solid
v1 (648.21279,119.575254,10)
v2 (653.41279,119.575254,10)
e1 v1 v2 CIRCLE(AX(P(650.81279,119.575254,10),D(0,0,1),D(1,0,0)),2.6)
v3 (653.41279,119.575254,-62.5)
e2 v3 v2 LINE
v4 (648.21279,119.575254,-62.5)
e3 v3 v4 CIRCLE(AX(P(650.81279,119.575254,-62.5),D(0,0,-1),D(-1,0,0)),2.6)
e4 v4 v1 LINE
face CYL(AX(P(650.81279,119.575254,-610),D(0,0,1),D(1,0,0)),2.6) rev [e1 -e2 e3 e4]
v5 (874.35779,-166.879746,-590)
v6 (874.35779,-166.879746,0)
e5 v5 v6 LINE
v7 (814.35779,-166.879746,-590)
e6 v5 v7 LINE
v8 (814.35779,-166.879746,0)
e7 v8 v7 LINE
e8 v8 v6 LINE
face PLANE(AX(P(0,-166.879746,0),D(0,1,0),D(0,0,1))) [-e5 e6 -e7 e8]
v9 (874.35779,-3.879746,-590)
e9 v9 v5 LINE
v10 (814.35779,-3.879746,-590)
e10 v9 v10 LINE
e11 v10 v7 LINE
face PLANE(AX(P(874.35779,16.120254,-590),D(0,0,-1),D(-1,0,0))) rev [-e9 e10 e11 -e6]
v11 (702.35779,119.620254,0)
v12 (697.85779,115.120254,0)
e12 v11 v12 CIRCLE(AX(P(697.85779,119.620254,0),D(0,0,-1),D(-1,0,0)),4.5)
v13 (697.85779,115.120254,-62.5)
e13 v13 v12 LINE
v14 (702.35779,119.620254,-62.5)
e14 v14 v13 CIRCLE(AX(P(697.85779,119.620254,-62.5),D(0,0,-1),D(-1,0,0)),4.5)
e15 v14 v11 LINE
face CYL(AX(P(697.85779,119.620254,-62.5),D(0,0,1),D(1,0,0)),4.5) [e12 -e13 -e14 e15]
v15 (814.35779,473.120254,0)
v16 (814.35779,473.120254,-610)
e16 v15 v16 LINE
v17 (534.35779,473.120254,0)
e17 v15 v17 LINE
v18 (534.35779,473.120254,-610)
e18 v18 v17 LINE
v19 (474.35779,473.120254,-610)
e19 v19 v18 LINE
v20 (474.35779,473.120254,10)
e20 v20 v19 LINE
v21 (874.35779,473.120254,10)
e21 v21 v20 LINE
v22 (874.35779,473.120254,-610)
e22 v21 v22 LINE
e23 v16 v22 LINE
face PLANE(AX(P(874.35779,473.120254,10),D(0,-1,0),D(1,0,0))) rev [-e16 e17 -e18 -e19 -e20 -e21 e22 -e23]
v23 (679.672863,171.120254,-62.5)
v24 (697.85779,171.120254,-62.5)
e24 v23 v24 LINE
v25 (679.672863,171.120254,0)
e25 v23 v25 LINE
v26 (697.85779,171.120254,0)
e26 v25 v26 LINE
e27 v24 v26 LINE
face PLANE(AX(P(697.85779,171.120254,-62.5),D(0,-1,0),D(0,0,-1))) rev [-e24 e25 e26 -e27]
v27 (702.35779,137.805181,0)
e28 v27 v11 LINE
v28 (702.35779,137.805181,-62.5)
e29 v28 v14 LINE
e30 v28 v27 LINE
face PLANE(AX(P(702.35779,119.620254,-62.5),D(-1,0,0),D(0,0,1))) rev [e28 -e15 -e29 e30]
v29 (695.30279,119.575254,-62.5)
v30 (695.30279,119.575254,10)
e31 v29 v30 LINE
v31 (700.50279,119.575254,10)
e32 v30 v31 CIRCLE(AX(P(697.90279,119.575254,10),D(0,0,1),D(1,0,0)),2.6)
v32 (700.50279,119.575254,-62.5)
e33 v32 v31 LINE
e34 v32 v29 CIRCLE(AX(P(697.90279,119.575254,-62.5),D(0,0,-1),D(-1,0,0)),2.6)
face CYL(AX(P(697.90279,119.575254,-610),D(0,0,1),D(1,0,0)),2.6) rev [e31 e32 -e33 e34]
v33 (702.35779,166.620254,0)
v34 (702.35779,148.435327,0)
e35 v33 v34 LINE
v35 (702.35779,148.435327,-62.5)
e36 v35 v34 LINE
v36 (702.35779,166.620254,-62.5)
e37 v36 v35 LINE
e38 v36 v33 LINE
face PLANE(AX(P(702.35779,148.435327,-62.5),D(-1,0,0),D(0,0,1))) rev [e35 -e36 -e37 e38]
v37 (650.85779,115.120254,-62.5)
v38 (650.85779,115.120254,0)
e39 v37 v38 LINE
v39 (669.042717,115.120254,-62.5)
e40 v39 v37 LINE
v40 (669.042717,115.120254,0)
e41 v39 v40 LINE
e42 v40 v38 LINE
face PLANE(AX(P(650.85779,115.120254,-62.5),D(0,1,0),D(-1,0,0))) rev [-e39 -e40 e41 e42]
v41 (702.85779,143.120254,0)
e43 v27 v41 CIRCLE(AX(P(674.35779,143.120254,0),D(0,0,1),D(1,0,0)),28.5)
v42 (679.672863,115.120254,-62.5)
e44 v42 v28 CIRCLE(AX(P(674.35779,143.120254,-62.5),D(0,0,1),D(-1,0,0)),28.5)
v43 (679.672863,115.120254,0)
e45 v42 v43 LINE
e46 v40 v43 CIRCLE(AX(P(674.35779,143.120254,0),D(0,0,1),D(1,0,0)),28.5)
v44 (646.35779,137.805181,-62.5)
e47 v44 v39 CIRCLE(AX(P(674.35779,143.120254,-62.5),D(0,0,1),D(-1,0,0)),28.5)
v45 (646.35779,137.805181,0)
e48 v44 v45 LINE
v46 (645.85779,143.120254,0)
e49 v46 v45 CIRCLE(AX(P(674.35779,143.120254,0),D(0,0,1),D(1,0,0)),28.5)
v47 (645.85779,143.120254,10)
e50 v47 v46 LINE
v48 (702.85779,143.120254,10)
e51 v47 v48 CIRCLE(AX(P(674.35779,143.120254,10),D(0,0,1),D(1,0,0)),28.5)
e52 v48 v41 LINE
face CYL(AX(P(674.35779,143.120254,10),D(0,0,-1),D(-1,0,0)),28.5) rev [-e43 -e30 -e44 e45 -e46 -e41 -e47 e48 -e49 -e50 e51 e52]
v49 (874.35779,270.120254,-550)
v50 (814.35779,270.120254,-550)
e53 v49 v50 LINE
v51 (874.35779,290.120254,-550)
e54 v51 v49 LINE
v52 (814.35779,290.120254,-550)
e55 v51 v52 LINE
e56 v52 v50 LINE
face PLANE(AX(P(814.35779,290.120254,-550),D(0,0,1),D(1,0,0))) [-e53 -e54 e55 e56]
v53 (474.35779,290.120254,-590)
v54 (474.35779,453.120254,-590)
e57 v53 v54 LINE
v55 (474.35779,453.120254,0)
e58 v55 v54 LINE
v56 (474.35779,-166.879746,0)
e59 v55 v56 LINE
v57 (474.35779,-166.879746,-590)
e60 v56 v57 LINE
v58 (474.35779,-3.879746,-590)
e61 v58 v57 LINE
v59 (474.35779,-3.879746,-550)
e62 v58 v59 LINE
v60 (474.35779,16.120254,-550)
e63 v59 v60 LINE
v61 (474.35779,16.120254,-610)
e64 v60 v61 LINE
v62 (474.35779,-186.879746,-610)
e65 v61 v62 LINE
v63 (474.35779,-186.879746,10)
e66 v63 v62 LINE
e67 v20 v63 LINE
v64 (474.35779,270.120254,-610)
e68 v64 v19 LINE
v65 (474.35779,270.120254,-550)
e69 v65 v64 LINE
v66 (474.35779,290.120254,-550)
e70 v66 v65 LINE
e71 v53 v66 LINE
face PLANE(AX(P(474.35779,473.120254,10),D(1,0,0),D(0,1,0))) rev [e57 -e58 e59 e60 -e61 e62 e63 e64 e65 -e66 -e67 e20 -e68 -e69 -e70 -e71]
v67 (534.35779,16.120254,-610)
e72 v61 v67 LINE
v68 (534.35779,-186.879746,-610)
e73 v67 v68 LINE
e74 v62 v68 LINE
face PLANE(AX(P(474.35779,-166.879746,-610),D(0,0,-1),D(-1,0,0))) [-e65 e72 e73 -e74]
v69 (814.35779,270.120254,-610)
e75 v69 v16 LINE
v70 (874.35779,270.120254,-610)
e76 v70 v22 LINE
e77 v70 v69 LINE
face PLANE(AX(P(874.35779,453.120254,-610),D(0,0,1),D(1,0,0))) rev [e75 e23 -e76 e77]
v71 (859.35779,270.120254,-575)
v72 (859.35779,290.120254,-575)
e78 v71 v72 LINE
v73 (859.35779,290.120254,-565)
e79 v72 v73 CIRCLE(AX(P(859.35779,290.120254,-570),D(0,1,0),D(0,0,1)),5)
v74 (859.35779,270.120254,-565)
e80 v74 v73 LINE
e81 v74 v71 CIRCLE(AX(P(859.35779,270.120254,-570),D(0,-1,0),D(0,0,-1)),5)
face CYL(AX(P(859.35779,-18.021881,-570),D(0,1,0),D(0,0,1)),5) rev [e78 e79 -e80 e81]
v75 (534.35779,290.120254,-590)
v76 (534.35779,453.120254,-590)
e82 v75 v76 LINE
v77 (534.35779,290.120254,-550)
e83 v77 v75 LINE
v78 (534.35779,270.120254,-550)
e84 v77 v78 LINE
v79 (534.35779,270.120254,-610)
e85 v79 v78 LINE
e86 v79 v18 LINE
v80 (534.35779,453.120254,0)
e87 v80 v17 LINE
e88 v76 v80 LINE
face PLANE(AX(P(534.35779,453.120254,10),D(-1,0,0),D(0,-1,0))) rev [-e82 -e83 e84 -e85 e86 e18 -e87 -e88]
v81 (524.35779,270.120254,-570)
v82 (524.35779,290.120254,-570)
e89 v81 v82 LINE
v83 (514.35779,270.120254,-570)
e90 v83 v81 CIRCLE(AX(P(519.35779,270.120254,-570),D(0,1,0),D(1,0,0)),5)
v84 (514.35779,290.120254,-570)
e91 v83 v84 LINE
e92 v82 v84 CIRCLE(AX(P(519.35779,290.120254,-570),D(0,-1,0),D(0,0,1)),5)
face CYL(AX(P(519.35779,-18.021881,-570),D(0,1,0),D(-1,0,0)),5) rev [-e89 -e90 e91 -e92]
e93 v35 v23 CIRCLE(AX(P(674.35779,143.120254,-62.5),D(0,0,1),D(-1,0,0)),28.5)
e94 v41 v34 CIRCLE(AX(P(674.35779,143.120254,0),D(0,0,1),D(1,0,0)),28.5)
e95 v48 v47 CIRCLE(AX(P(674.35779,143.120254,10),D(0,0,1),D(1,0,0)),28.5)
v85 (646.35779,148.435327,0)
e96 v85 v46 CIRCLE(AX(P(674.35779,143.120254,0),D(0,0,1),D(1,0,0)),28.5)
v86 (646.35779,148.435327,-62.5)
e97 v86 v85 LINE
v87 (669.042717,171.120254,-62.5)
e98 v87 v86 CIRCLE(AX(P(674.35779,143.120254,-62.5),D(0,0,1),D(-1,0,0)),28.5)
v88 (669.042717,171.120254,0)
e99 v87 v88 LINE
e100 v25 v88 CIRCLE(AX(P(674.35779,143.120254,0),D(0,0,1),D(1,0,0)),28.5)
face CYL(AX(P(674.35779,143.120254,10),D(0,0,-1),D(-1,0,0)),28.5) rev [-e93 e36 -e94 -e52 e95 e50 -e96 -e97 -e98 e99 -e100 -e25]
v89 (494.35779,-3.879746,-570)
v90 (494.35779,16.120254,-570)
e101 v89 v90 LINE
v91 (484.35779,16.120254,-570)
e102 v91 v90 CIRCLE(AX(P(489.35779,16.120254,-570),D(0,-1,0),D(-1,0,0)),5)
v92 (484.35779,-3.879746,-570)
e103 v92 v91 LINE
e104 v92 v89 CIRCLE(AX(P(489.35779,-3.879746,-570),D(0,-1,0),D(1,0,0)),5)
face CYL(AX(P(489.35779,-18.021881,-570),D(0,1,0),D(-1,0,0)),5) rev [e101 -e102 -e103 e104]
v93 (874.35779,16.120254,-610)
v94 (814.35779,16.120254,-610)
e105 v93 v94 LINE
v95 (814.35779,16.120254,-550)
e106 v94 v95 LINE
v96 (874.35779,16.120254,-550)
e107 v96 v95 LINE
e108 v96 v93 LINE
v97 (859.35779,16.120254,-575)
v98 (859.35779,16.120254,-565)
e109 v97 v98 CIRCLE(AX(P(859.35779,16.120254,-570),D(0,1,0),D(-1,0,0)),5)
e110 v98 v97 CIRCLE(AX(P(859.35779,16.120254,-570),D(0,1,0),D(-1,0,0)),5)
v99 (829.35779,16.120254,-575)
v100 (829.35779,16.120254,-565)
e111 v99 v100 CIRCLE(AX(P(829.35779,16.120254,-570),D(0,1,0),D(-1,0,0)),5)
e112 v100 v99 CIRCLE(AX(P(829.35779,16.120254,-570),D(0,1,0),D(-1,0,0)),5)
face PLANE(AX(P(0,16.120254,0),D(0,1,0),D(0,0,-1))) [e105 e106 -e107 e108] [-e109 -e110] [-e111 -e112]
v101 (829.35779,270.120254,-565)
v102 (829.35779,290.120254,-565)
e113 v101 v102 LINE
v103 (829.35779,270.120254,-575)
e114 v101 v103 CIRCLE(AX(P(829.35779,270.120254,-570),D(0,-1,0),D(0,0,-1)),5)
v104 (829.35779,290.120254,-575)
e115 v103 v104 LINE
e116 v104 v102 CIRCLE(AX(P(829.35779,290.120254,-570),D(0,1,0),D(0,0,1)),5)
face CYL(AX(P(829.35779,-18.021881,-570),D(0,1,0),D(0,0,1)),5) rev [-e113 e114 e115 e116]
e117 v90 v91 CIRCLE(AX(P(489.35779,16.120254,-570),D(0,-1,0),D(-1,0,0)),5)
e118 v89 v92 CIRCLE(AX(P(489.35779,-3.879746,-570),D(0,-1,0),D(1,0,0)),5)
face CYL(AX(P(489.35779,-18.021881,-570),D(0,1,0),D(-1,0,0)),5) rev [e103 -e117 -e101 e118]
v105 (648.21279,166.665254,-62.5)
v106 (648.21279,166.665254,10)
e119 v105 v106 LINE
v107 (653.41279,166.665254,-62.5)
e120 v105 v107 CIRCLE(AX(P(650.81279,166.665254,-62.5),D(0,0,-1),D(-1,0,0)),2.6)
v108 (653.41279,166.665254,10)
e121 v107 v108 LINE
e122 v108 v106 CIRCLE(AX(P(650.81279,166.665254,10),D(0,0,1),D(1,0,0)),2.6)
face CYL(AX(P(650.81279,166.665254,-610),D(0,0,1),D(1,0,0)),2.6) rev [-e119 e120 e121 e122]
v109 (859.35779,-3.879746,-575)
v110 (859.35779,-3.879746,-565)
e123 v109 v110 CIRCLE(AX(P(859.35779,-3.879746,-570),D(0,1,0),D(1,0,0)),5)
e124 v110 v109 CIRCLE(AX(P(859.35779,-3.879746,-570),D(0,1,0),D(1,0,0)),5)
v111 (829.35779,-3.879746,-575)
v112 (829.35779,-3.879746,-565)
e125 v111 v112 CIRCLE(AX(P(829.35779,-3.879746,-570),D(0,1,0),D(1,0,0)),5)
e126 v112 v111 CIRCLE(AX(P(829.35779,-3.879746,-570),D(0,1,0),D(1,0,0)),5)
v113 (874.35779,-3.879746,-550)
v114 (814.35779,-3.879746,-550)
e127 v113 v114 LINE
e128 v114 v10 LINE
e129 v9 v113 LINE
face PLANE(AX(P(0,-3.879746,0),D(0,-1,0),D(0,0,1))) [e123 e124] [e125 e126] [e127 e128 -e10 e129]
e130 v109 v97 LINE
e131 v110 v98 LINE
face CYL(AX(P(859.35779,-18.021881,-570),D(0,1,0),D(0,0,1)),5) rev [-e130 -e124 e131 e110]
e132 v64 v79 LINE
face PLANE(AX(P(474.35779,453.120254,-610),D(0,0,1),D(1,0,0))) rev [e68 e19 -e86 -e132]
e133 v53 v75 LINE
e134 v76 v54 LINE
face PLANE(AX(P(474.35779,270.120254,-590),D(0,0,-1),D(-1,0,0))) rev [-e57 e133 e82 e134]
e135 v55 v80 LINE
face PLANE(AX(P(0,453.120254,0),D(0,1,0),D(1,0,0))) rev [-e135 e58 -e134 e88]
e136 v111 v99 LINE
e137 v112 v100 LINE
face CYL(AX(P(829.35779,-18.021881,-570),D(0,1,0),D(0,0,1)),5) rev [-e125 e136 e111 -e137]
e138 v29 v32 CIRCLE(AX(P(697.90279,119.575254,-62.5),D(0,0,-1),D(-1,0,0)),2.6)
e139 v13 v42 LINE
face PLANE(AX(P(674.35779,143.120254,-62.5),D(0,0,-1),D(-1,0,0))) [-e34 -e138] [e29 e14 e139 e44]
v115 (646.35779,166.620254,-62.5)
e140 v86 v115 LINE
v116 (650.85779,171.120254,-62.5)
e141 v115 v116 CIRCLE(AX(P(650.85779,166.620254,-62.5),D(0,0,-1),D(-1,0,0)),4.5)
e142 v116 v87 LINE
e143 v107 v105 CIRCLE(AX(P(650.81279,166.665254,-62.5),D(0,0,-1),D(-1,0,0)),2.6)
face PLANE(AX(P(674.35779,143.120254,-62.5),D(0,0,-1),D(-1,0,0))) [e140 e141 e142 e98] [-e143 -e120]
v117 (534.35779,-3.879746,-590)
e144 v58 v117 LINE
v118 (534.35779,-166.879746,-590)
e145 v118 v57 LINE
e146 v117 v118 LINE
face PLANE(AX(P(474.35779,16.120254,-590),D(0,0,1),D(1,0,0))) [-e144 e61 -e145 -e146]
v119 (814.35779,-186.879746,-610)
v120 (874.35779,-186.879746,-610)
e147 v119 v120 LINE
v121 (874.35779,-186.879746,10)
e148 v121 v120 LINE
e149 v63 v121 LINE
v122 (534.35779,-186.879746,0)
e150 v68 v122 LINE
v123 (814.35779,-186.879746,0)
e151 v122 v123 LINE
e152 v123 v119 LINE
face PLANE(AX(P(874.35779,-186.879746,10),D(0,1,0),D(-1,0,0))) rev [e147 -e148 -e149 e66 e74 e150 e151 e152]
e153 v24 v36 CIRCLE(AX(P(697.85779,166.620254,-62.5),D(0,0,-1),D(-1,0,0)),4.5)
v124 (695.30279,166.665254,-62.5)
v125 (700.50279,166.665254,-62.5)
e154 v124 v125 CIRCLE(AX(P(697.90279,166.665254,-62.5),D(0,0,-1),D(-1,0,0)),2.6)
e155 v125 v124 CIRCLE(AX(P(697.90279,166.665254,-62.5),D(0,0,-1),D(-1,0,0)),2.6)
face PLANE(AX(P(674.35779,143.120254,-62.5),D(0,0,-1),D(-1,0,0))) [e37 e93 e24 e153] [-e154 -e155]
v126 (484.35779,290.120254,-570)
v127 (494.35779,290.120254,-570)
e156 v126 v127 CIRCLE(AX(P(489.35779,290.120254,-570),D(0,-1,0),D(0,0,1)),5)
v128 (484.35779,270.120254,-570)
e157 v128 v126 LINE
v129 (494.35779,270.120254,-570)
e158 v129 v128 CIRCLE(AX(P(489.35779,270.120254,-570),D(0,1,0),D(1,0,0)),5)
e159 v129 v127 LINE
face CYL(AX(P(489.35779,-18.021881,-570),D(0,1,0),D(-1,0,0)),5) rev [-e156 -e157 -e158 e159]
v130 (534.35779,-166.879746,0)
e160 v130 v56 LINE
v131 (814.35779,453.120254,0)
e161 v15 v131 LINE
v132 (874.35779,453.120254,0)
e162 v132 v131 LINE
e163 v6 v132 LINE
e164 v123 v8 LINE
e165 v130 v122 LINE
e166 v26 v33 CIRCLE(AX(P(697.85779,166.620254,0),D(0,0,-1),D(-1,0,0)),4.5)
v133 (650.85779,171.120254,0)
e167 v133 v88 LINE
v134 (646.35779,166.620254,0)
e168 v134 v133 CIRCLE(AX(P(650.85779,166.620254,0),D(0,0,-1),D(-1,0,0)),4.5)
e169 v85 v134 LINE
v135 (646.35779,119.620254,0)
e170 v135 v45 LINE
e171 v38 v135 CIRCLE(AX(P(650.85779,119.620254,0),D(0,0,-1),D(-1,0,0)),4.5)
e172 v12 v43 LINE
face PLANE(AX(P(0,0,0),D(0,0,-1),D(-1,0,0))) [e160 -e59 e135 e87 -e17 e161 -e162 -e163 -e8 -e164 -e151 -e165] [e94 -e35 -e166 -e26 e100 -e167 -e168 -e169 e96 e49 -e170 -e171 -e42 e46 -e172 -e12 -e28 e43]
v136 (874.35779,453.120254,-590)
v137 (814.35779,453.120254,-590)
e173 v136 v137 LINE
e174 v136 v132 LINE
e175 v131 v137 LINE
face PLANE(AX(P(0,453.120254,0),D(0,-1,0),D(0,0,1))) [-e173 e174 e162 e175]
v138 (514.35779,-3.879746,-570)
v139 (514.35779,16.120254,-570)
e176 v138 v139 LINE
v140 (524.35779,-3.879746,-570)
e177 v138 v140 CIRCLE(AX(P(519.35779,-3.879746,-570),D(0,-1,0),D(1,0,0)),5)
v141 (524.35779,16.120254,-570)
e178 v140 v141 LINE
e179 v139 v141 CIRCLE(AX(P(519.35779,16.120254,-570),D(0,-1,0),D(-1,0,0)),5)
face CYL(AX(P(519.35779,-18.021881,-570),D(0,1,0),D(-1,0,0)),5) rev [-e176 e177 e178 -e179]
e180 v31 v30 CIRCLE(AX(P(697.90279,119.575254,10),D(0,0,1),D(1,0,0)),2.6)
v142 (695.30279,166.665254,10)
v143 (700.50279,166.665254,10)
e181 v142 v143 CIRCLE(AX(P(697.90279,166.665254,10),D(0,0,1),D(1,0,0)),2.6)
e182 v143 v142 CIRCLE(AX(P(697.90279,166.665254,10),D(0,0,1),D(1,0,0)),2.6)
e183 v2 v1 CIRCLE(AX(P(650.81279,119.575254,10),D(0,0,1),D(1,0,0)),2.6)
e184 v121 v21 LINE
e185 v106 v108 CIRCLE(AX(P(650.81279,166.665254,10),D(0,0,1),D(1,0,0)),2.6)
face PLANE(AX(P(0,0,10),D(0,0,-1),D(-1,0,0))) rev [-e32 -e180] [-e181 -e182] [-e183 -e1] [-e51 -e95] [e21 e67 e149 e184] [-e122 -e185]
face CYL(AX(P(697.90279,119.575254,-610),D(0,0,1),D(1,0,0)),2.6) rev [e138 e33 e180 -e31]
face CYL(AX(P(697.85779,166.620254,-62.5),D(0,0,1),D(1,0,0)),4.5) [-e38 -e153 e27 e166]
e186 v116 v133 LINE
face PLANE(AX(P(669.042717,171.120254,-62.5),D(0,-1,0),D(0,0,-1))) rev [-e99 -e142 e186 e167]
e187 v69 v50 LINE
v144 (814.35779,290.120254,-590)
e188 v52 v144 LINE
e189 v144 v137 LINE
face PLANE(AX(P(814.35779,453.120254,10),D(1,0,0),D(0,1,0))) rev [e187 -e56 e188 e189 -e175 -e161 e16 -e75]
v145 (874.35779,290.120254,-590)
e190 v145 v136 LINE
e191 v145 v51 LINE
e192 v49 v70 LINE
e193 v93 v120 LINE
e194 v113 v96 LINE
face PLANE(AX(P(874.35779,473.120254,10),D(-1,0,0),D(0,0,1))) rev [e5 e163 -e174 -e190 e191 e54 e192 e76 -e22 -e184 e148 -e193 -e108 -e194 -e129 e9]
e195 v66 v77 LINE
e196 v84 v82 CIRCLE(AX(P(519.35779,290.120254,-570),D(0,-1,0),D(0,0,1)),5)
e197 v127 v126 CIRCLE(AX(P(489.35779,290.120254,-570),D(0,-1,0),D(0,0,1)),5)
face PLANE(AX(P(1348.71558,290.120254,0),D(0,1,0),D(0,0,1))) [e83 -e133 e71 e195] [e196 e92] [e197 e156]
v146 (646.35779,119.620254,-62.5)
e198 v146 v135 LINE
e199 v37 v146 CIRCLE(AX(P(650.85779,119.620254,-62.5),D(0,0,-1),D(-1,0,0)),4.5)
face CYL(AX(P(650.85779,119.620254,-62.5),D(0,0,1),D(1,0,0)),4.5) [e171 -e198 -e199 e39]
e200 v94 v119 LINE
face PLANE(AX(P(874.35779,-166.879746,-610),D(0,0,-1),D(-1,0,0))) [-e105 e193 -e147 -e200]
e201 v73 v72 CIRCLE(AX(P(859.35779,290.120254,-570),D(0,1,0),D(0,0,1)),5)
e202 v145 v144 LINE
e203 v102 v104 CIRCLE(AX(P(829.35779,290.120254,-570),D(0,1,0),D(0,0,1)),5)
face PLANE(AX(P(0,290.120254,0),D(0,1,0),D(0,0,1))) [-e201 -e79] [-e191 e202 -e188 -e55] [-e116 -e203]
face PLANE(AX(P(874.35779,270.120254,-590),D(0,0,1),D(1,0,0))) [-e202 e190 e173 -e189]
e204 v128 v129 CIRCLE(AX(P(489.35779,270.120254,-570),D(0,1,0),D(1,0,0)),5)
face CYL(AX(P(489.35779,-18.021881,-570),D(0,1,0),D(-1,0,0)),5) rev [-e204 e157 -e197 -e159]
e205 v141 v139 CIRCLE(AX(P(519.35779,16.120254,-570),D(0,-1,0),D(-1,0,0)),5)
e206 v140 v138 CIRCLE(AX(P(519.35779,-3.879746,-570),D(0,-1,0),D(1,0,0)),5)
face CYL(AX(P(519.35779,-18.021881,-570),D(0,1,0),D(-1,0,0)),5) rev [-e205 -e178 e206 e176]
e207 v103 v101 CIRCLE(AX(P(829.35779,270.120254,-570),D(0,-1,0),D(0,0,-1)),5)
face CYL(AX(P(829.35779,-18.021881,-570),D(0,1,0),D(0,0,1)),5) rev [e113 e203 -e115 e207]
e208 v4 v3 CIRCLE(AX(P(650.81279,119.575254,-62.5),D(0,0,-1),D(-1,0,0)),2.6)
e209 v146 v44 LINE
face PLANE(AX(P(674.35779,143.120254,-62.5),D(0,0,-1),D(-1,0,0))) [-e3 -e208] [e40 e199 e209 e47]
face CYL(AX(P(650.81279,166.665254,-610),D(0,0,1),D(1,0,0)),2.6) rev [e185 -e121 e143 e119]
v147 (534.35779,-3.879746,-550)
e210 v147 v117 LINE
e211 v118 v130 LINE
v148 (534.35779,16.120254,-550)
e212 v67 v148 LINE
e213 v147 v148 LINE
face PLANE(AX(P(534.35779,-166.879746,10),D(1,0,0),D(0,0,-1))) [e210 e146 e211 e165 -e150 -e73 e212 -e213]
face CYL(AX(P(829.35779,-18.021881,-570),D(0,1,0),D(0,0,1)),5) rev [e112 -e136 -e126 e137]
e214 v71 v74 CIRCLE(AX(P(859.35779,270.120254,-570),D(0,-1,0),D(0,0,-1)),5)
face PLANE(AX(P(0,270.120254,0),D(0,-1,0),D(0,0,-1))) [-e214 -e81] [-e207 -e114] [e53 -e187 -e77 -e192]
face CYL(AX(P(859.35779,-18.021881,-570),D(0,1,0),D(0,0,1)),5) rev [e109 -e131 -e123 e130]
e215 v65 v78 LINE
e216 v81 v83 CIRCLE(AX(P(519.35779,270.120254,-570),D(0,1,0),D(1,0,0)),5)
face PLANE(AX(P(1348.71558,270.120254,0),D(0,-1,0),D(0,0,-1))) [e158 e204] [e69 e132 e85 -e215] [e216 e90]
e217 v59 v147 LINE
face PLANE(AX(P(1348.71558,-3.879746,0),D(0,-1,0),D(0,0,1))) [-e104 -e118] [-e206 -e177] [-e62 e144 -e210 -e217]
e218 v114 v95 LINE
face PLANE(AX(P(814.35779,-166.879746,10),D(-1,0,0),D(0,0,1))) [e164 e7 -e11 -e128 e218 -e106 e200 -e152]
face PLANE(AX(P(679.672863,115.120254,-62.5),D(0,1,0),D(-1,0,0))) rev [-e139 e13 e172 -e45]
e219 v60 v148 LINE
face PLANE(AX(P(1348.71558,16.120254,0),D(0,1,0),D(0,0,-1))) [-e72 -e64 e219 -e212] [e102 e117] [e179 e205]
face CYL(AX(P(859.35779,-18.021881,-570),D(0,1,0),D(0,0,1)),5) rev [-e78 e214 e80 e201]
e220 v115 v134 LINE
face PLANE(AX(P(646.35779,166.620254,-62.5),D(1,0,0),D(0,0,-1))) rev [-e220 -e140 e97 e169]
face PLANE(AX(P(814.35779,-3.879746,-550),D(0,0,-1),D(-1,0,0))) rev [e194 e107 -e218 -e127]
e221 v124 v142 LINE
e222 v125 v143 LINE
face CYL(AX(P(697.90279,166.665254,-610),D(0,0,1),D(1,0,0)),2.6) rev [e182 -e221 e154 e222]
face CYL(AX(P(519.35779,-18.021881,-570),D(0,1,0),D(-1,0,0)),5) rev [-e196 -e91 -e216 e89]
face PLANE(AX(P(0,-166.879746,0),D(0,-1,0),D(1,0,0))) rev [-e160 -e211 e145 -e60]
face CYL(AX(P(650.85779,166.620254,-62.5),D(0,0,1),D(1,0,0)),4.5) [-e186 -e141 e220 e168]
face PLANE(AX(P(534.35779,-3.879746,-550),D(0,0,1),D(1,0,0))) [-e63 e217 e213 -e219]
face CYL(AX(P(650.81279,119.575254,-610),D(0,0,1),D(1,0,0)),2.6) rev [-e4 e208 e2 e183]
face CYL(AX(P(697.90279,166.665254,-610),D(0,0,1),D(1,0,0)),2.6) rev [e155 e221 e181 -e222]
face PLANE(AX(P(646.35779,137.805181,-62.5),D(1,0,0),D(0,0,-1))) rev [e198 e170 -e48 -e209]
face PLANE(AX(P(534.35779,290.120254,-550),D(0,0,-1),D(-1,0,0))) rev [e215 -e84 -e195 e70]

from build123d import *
from build123d.topology import SkipClean

# Parameters (mm, degrees)
SKETCH_1_W                                 = 400
SKETCH_1_H                                 = 660
SKETCH_1_R                                 = 28.5
EXTRUDE_1_DEPTH                            = 10
EXTRUDE_START                              = 62.5
EXTRUDE_3_DEPTH                            = 62.5
SKETCH_4_W                                 = 60
SKETCH_4_H                                 = 620
EXTRUDE_4_DEPTH                            = 20
SKETCH_5_W                                 = 60
SKETCH_5_H                                 = 20
EXTRUDE_5_DEPTH                            = 203
MIRROR_3_COPY_1_SKETCH_W                   = 60
MIRROR_3_COPY_1_SKETCH_H                   = 20
MIRROR_3_COPY_1_DEPTH                      = 203
MIRROR_3_AT_THE_SECOND_PLANE_COPY_1_SKET_W = 60
MIRROR_3_AT_THE_SECOND_PLANE_COPY_1_SKET_H = 20
MIRROR_3_AT_THE_SECOND_PLANE_COPY_1_DEPTH  = 203
MIRROR_3_AT_THE_SECOND_PLANE_COPY_2_SKET_W = 60
MIRROR_3_AT_THE_SECOND_PLANE_COPY_2_SKET_H = 20
MIRROR_3_AT_THE_SECOND_PLANE_COPY_2_DEPTH  = 203
MIRROR_3_AT_THE_SECOND_PLANE_COPY_3_SKET_W = 60
MIRROR_3_AT_THE_SECOND_PLANE_COPY_3_SKET_H = 20
MIRROR_3_AT_THE_SECOND_PLANE_COPY_3_DEPTH  = 203
SKETCH_6_W                                 = 60
SKETCH_6_H                                 = 60
EXTRUDE_6_DEPTH                            = 20
MIRROR_5_COPY_1_SKETCH_W                   = 60
MIRROR_5_COPY_1_SKETCH_H                   = 60
MIRROR_5_COPY_1_DEPTH                      = 20
CUT_EXTRUDE_1_REACH                        = 1169.96
SKETCH_7_R                                 = 5
SKETCH_8_R                                 = 2.6
CUT_EXTRUDE_2_DEPTH                        = 1172.641719812


with BuildPart() as part:
    # 草图1 → 凸台-拉伸1 (new body)
    with BuildSketch(Plane.XY):
        with Locations((674.357789758, 143.120254367)):
            Rectangle(SKETCH_1_W, SKETCH_1_H)
        with Locations((674.357789758, 143.120254367)):
            Circle(SKETCH_1_R, mode=Mode.SUBTRACT)
    extrude(amount=EXTRUDE_1_DEPTH)

    # 草图3 → 凸台-拉伸3 (add)
    with SkipClean():  # the faces are left unmerged after this step: merging them gives an invalid solid
        with BuildSketch(Plane(origin=(0, 0, 0), x_dir=(-1, 0, 0), z_dir=(0, 0, -1)).offset(EXTRUDE_START)):
            with BuildLine():
                Line((-702.357789758, 148.435327273), (-702.357789758, 166.620254367))
                ThreePointArc((-702.357789758, 166.620254367), (-701.039770274, 169.802234882), (-697.857789758, 171.120254367))
                Line((-697.857789758, 171.120254367), (-679.672862665, 171.120254367))
                ThreePointArc((-679.672862665, 171.120254367), (-694.510333022, 163.27279763), (-702.357789758, 148.435327273))
            make_face()
            with BuildLine():
                Line((-679.672862665, 115.120254367), (-697.857789758, 115.120254367))
                ThreePointArc((-697.857789758, 115.120254367), (-701.039770274, 116.438273851), (-702.357789758, 119.620254367))
                Line((-702.357789758, 119.620254367), (-702.357789758, 137.80518146))
                ThreePointArc((-702.357789758, 137.80518146), (-694.510333022, 122.967711103), (-679.672862665, 115.120254367))
            make_face()
            with BuildLine():
                Line((-646.357789758, 137.80518146), (-646.357789758, 119.620254367))
                ThreePointArc((-646.357789758, 119.620254367), (-647.675809243, 116.438273851), (-650.857789758, 115.120254367))
                Line((-650.857789758, 115.120254367), (-669.042716852, 115.120254367))
                ThreePointArc((-669.042716852, 115.120254367), (-654.205246495, 122.967711103), (-646.357789758, 137.80518146))
            make_face()
            with BuildLine():
                Line((-669.042716852, 171.120254367), (-650.857789758, 171.120254367))
                ThreePointArc((-650.857789758, 171.120254367), (-647.675809243, 169.802234882), (-646.357789758, 166.620254367))
                Line((-646.357789758, 166.620254367), (-646.357789758, 148.435327273))
                ThreePointArc((-646.357789758, 148.435327273), (-654.205246495, 163.27279763), (-669.042716852, 171.120254367))
            make_face()
        extrude(amount=-EXTRUDE_3_DEPTH)

    # 草图4 → 凸台-拉伸4 (add)
    with SkipClean():  # the faces are left unmerged after this step: merging them gives an invalid solid
        with BuildSketch(Plane.XZ.offset(186.879745633)):
            with Locations((504.357789758, -300)):
                Rectangle(SKETCH_4_W, SKETCH_4_H)
            with Locations((844.357789758, -300)):
                Rectangle(SKETCH_4_W, SKETCH_4_H)
        extrude_4 = extrude(amount=-EXTRUDE_4_DEPTH)

    # 镜向1: 凸台-拉伸4 across plane
    with SkipClean():  # the faces are left unmerged after this step: merging them gives an invalid solid
        add(extrude_4.mirror(Plane(origin=(0, 143.120254367, 0), x_dir=(0, 0, 1), z_dir=(0, -1, 0))))

    # 草图5 → 凸台-拉伸5 (add)
    with SkipClean():  # the faces are left unmerged after this step: merging them gives an invalid solid
        with BuildSketch(Plane(origin=(0, 473.120254367, 0), x_dir=(1, 0, 0), z_dir=(0, 1, 0))):
            with Locations((844.357789758, 600)):
                Rectangle(SKETCH_5_W, SKETCH_5_H)
        extrude_5 = extrude(amount=-EXTRUDE_5_DEPTH)

    # 镜向2: 凸台-拉伸5 across plane
    with SkipClean():  # the faces are left unmerged after this step: merging them gives an invalid solid
        add(extrude_5.mirror(Plane(origin=(674.357789758, 0, 0), x_dir=(0, 0, 1), z_dir=(1, 0, 0))))

    # 镜向3: 凸台-拉伸5 across plane
    with SkipClean():  # the faces are left unmerged after this step: merging them gives an invalid solid
        add(extrude_5.mirror(Plane(origin=(0, 143.120254367, 0), x_dir=(0, 0, 1), z_dir=(0, -1, 0))))

    # 镜向3 copy 1 sketch → 镜向3 copy 1 (add)
    with SkipClean():  # the faces are left unmerged after this step: merging them gives an invalid solid
        with BuildSketch(Plane(origin=(1348.715579517, -186.879745633, 0), x_dir=(-1, 0, 0), z_dir=(0, -1, 0))):
            with Locations((844.357789758, 600)):
                Rectangle(MIRROR_3_COPY_1_SKETCH_W, MIRROR_3_COPY_1_SKETCH_H)
        extrude(amount=-MIRROR_3_COPY_1_DEPTH)

    # 镜向3 at the second plane: 凸台-拉伸5 across plane
    with SkipClean():  # the faces are left unmerged after this step: merging them gives an invalid solid
        add(extrude_5.mirror(Plane(origin=(674.357789758, 0, 0), x_dir=(0, 0, 1), z_dir=(1, 0, 0))))

    # 镜向3 at the second plane copy 1 sket → 镜向3 at the second plane copy 1 (add)
    with SkipClean():  # the faces are left unmerged after this step: merging them gives an invalid solid
        with BuildSketch(Plane(origin=(0, 473.120254367, 0), x_dir=(1, 0, 0), z_dir=(0, 1, 0))):
            with Locations((844.357789758, 600)):
                Rectangle(MIRROR_3_AT_THE_SECOND_PLANE_COPY_1_SKET_W, MIRROR_3_AT_THE_SECOND_PLANE_COPY_1_SKET_H)
        extrude(amount=-MIRROR_3_AT_THE_SECOND_PLANE_COPY_1_DEPTH)

    # 镜向3 at the second plane copy 2 sket → 镜向3 at the second plane copy 2 (add)
    with SkipClean():  # the faces are left unmerged after this step: merging them gives an invalid solid
        with BuildSketch(Plane(origin=(1348.715579517, -186.879745633, 0), x_dir=(-1, 0, 0), z_dir=(0, -1, 0))):
            with Locations((844.357789758, 600)):
                Rectangle(MIRROR_3_AT_THE_SECOND_PLANE_COPY_2_SKET_W, MIRROR_3_AT_THE_SECOND_PLANE_COPY_2_SKET_H)
        extrude(amount=-MIRROR_3_AT_THE_SECOND_PLANE_COPY_2_DEPTH)

    # 镜向3 at the second plane copy 3 sket → 镜向3 at the second plane copy 3 (add)
    with SkipClean():  # the faces are left unmerged after this step: merging them gives an invalid solid
        with BuildSketch(Plane.XZ.offset(186.879745633)):
            with Locations((844.357789758, -600)):
                Rectangle(MIRROR_3_AT_THE_SECOND_PLANE_COPY_3_SKET_W, MIRROR_3_AT_THE_SECOND_PLANE_COPY_3_SKET_H)
        extrude(amount=-MIRROR_3_AT_THE_SECOND_PLANE_COPY_3_DEPTH)

    # 草图6 → 凸台-拉伸6 (add)
    with SkipClean():  # the faces are left unmerged after this step: merging them gives an invalid solid
        with BuildSketch(Plane.XZ.offset(-270.120254367)):
            with Locations((844.357789758, -580)):
                Rectangle(SKETCH_6_W, SKETCH_6_H)
        extrude_6 = extrude(amount=-EXTRUDE_6_DEPTH)

    # 镜向4: 凸台-拉伸6 across plane
    with SkipClean():  # the faces are left unmerged after this step: merging them gives an invalid solid
        add(extrude_6.mirror(Plane(origin=(674.357789758, 0, 0), x_dir=(0, 0, 1), z_dir=(1, 0, 0))))

    # 镜向5: 凸台-拉伸6 across plane
    with SkipClean():  # the faces are left unmerged after this step: merging them gives an invalid solid
        add(extrude_6.mirror(Plane(origin=(0, 143.120254367, 0), x_dir=(0, 0, 1), z_dir=(0, -1, 0))))

    # 镜向5 copy 1 sketch → 镜向5 copy 1 (add)
    with SkipClean():  # the faces are left unmerged after this step: merging them gives an invalid solid
        with BuildSketch(Plane(origin=(1348.715579517, 16.120254367, 0), x_dir=(-1, 0, 0), z_dir=(0, 1, 0))):
            with Locations((844.357789758, -580)):
                Rectangle(MIRROR_5_COPY_1_SKETCH_W, MIRROR_5_COPY_1_SKETCH_H)
        extrude(amount=-MIRROR_5_COPY_1_DEPTH)

    # 切除-拉伸1: up to this face of the body (flat: up to its plane)
    cut_extrude_1_end = Plane(part.part.faces().sort_by_distance((844.357789758, -3.879745633, -570))[0])
    # 草图7 → 切除-拉伸1 (cut, up to the picked face)
    with BuildSketch(Plane(origin=(0, 290.120254367, 0), x_dir=(1, 0, 0), z_dir=(0, 1, 0)), mode=Mode.PRIVATE) as cut_extrude_1_sk1:
        with Locations(Location((859.357789758, 570, 0), (0, 0, 180))):
            Circle(SKETCH_7_R)
    cut_extrude_1_tool1 = split(extrude(cut_extrude_1_sk1.sketch, amount=-CUT_EXTRUDE_1_REACH, mode=Mode.PRIVATE), bisect_by=cut_extrude_1_end, keep=Keep.BOTH, mode=Mode.PRIVATE)
    # 草图7 → 切除-拉伸1 (cut, up to the picked face)
    with BuildSketch(Plane(origin=(0, 290.120254367, 0), x_dir=(1, 0, 0), z_dir=(0, 1, 0)), mode=Mode.PRIVATE) as cut_extrude_1_sk2:
        with Locations(Location((829.357789758, 570, 0), (0, 0, 180))):
            Circle(SKETCH_7_R)
    cut_extrude_1_tool2 = split(extrude(cut_extrude_1_sk2.sketch, amount=-CUT_EXTRUDE_1_REACH, mode=Mode.PRIVATE), bisect_by=cut_extrude_1_end, keep=Keep.BOTH, mode=Mode.PRIVATE)
    cut_extrude_1_1 = cut_extrude_1_tool1.solids().sort_by(Axis((859.35779, 290.120254, -570), (0, -1, 0)))[0]
    add(cut_extrude_1_1, mode=Mode.SUBTRACT)
    cut_extrude_1_2 = cut_extrude_1_tool2.solids().sort_by(Axis((829.35779, 290.120254, -570), (0, -1, 0)))[0]
    add(cut_extrude_1_2, mode=Mode.SUBTRACT)
    cut_extrude_1 = cut_extrude_1_1 + cut_extrude_1_2  # 切除-拉伸1 as one shape, for the pattern or mirror that repeats it

    # 镜向6: 切除-拉伸1 across plane
    with SkipClean():  # the faces are left unmerged after this step: merging them gives an invalid solid
        add(cut_extrude_1.mirror(Plane(origin=(674.357789758, 0, 0), x_dir=(0, 0, 1), z_dir=(1, 0, 0))), mode=Mode.SUBTRACT)

    # 草图8 → 切除-拉伸2 (cut, through all)
    with SkipClean():  # the faces are left unmerged after this step: merging them gives an invalid solid
        with BuildSketch(Plane.XY.offset(10)):
            with Locations((650.812789758, 166.665254367)):
                Circle(SKETCH_8_R)
            with Locations((650.812789758, 119.575254367)):
                Circle(SKETCH_8_R)
            with Locations((697.902789758, 119.575254367)):
                Circle(SKETCH_8_R)
            with Locations((697.902789758, 166.665254367)):
                Circle(SKETCH_8_R)
        extrude(amount=-CUT_EXTRUDE_2_DEPTH, mode=Mode.SUBTRACT)


solid = part.part
